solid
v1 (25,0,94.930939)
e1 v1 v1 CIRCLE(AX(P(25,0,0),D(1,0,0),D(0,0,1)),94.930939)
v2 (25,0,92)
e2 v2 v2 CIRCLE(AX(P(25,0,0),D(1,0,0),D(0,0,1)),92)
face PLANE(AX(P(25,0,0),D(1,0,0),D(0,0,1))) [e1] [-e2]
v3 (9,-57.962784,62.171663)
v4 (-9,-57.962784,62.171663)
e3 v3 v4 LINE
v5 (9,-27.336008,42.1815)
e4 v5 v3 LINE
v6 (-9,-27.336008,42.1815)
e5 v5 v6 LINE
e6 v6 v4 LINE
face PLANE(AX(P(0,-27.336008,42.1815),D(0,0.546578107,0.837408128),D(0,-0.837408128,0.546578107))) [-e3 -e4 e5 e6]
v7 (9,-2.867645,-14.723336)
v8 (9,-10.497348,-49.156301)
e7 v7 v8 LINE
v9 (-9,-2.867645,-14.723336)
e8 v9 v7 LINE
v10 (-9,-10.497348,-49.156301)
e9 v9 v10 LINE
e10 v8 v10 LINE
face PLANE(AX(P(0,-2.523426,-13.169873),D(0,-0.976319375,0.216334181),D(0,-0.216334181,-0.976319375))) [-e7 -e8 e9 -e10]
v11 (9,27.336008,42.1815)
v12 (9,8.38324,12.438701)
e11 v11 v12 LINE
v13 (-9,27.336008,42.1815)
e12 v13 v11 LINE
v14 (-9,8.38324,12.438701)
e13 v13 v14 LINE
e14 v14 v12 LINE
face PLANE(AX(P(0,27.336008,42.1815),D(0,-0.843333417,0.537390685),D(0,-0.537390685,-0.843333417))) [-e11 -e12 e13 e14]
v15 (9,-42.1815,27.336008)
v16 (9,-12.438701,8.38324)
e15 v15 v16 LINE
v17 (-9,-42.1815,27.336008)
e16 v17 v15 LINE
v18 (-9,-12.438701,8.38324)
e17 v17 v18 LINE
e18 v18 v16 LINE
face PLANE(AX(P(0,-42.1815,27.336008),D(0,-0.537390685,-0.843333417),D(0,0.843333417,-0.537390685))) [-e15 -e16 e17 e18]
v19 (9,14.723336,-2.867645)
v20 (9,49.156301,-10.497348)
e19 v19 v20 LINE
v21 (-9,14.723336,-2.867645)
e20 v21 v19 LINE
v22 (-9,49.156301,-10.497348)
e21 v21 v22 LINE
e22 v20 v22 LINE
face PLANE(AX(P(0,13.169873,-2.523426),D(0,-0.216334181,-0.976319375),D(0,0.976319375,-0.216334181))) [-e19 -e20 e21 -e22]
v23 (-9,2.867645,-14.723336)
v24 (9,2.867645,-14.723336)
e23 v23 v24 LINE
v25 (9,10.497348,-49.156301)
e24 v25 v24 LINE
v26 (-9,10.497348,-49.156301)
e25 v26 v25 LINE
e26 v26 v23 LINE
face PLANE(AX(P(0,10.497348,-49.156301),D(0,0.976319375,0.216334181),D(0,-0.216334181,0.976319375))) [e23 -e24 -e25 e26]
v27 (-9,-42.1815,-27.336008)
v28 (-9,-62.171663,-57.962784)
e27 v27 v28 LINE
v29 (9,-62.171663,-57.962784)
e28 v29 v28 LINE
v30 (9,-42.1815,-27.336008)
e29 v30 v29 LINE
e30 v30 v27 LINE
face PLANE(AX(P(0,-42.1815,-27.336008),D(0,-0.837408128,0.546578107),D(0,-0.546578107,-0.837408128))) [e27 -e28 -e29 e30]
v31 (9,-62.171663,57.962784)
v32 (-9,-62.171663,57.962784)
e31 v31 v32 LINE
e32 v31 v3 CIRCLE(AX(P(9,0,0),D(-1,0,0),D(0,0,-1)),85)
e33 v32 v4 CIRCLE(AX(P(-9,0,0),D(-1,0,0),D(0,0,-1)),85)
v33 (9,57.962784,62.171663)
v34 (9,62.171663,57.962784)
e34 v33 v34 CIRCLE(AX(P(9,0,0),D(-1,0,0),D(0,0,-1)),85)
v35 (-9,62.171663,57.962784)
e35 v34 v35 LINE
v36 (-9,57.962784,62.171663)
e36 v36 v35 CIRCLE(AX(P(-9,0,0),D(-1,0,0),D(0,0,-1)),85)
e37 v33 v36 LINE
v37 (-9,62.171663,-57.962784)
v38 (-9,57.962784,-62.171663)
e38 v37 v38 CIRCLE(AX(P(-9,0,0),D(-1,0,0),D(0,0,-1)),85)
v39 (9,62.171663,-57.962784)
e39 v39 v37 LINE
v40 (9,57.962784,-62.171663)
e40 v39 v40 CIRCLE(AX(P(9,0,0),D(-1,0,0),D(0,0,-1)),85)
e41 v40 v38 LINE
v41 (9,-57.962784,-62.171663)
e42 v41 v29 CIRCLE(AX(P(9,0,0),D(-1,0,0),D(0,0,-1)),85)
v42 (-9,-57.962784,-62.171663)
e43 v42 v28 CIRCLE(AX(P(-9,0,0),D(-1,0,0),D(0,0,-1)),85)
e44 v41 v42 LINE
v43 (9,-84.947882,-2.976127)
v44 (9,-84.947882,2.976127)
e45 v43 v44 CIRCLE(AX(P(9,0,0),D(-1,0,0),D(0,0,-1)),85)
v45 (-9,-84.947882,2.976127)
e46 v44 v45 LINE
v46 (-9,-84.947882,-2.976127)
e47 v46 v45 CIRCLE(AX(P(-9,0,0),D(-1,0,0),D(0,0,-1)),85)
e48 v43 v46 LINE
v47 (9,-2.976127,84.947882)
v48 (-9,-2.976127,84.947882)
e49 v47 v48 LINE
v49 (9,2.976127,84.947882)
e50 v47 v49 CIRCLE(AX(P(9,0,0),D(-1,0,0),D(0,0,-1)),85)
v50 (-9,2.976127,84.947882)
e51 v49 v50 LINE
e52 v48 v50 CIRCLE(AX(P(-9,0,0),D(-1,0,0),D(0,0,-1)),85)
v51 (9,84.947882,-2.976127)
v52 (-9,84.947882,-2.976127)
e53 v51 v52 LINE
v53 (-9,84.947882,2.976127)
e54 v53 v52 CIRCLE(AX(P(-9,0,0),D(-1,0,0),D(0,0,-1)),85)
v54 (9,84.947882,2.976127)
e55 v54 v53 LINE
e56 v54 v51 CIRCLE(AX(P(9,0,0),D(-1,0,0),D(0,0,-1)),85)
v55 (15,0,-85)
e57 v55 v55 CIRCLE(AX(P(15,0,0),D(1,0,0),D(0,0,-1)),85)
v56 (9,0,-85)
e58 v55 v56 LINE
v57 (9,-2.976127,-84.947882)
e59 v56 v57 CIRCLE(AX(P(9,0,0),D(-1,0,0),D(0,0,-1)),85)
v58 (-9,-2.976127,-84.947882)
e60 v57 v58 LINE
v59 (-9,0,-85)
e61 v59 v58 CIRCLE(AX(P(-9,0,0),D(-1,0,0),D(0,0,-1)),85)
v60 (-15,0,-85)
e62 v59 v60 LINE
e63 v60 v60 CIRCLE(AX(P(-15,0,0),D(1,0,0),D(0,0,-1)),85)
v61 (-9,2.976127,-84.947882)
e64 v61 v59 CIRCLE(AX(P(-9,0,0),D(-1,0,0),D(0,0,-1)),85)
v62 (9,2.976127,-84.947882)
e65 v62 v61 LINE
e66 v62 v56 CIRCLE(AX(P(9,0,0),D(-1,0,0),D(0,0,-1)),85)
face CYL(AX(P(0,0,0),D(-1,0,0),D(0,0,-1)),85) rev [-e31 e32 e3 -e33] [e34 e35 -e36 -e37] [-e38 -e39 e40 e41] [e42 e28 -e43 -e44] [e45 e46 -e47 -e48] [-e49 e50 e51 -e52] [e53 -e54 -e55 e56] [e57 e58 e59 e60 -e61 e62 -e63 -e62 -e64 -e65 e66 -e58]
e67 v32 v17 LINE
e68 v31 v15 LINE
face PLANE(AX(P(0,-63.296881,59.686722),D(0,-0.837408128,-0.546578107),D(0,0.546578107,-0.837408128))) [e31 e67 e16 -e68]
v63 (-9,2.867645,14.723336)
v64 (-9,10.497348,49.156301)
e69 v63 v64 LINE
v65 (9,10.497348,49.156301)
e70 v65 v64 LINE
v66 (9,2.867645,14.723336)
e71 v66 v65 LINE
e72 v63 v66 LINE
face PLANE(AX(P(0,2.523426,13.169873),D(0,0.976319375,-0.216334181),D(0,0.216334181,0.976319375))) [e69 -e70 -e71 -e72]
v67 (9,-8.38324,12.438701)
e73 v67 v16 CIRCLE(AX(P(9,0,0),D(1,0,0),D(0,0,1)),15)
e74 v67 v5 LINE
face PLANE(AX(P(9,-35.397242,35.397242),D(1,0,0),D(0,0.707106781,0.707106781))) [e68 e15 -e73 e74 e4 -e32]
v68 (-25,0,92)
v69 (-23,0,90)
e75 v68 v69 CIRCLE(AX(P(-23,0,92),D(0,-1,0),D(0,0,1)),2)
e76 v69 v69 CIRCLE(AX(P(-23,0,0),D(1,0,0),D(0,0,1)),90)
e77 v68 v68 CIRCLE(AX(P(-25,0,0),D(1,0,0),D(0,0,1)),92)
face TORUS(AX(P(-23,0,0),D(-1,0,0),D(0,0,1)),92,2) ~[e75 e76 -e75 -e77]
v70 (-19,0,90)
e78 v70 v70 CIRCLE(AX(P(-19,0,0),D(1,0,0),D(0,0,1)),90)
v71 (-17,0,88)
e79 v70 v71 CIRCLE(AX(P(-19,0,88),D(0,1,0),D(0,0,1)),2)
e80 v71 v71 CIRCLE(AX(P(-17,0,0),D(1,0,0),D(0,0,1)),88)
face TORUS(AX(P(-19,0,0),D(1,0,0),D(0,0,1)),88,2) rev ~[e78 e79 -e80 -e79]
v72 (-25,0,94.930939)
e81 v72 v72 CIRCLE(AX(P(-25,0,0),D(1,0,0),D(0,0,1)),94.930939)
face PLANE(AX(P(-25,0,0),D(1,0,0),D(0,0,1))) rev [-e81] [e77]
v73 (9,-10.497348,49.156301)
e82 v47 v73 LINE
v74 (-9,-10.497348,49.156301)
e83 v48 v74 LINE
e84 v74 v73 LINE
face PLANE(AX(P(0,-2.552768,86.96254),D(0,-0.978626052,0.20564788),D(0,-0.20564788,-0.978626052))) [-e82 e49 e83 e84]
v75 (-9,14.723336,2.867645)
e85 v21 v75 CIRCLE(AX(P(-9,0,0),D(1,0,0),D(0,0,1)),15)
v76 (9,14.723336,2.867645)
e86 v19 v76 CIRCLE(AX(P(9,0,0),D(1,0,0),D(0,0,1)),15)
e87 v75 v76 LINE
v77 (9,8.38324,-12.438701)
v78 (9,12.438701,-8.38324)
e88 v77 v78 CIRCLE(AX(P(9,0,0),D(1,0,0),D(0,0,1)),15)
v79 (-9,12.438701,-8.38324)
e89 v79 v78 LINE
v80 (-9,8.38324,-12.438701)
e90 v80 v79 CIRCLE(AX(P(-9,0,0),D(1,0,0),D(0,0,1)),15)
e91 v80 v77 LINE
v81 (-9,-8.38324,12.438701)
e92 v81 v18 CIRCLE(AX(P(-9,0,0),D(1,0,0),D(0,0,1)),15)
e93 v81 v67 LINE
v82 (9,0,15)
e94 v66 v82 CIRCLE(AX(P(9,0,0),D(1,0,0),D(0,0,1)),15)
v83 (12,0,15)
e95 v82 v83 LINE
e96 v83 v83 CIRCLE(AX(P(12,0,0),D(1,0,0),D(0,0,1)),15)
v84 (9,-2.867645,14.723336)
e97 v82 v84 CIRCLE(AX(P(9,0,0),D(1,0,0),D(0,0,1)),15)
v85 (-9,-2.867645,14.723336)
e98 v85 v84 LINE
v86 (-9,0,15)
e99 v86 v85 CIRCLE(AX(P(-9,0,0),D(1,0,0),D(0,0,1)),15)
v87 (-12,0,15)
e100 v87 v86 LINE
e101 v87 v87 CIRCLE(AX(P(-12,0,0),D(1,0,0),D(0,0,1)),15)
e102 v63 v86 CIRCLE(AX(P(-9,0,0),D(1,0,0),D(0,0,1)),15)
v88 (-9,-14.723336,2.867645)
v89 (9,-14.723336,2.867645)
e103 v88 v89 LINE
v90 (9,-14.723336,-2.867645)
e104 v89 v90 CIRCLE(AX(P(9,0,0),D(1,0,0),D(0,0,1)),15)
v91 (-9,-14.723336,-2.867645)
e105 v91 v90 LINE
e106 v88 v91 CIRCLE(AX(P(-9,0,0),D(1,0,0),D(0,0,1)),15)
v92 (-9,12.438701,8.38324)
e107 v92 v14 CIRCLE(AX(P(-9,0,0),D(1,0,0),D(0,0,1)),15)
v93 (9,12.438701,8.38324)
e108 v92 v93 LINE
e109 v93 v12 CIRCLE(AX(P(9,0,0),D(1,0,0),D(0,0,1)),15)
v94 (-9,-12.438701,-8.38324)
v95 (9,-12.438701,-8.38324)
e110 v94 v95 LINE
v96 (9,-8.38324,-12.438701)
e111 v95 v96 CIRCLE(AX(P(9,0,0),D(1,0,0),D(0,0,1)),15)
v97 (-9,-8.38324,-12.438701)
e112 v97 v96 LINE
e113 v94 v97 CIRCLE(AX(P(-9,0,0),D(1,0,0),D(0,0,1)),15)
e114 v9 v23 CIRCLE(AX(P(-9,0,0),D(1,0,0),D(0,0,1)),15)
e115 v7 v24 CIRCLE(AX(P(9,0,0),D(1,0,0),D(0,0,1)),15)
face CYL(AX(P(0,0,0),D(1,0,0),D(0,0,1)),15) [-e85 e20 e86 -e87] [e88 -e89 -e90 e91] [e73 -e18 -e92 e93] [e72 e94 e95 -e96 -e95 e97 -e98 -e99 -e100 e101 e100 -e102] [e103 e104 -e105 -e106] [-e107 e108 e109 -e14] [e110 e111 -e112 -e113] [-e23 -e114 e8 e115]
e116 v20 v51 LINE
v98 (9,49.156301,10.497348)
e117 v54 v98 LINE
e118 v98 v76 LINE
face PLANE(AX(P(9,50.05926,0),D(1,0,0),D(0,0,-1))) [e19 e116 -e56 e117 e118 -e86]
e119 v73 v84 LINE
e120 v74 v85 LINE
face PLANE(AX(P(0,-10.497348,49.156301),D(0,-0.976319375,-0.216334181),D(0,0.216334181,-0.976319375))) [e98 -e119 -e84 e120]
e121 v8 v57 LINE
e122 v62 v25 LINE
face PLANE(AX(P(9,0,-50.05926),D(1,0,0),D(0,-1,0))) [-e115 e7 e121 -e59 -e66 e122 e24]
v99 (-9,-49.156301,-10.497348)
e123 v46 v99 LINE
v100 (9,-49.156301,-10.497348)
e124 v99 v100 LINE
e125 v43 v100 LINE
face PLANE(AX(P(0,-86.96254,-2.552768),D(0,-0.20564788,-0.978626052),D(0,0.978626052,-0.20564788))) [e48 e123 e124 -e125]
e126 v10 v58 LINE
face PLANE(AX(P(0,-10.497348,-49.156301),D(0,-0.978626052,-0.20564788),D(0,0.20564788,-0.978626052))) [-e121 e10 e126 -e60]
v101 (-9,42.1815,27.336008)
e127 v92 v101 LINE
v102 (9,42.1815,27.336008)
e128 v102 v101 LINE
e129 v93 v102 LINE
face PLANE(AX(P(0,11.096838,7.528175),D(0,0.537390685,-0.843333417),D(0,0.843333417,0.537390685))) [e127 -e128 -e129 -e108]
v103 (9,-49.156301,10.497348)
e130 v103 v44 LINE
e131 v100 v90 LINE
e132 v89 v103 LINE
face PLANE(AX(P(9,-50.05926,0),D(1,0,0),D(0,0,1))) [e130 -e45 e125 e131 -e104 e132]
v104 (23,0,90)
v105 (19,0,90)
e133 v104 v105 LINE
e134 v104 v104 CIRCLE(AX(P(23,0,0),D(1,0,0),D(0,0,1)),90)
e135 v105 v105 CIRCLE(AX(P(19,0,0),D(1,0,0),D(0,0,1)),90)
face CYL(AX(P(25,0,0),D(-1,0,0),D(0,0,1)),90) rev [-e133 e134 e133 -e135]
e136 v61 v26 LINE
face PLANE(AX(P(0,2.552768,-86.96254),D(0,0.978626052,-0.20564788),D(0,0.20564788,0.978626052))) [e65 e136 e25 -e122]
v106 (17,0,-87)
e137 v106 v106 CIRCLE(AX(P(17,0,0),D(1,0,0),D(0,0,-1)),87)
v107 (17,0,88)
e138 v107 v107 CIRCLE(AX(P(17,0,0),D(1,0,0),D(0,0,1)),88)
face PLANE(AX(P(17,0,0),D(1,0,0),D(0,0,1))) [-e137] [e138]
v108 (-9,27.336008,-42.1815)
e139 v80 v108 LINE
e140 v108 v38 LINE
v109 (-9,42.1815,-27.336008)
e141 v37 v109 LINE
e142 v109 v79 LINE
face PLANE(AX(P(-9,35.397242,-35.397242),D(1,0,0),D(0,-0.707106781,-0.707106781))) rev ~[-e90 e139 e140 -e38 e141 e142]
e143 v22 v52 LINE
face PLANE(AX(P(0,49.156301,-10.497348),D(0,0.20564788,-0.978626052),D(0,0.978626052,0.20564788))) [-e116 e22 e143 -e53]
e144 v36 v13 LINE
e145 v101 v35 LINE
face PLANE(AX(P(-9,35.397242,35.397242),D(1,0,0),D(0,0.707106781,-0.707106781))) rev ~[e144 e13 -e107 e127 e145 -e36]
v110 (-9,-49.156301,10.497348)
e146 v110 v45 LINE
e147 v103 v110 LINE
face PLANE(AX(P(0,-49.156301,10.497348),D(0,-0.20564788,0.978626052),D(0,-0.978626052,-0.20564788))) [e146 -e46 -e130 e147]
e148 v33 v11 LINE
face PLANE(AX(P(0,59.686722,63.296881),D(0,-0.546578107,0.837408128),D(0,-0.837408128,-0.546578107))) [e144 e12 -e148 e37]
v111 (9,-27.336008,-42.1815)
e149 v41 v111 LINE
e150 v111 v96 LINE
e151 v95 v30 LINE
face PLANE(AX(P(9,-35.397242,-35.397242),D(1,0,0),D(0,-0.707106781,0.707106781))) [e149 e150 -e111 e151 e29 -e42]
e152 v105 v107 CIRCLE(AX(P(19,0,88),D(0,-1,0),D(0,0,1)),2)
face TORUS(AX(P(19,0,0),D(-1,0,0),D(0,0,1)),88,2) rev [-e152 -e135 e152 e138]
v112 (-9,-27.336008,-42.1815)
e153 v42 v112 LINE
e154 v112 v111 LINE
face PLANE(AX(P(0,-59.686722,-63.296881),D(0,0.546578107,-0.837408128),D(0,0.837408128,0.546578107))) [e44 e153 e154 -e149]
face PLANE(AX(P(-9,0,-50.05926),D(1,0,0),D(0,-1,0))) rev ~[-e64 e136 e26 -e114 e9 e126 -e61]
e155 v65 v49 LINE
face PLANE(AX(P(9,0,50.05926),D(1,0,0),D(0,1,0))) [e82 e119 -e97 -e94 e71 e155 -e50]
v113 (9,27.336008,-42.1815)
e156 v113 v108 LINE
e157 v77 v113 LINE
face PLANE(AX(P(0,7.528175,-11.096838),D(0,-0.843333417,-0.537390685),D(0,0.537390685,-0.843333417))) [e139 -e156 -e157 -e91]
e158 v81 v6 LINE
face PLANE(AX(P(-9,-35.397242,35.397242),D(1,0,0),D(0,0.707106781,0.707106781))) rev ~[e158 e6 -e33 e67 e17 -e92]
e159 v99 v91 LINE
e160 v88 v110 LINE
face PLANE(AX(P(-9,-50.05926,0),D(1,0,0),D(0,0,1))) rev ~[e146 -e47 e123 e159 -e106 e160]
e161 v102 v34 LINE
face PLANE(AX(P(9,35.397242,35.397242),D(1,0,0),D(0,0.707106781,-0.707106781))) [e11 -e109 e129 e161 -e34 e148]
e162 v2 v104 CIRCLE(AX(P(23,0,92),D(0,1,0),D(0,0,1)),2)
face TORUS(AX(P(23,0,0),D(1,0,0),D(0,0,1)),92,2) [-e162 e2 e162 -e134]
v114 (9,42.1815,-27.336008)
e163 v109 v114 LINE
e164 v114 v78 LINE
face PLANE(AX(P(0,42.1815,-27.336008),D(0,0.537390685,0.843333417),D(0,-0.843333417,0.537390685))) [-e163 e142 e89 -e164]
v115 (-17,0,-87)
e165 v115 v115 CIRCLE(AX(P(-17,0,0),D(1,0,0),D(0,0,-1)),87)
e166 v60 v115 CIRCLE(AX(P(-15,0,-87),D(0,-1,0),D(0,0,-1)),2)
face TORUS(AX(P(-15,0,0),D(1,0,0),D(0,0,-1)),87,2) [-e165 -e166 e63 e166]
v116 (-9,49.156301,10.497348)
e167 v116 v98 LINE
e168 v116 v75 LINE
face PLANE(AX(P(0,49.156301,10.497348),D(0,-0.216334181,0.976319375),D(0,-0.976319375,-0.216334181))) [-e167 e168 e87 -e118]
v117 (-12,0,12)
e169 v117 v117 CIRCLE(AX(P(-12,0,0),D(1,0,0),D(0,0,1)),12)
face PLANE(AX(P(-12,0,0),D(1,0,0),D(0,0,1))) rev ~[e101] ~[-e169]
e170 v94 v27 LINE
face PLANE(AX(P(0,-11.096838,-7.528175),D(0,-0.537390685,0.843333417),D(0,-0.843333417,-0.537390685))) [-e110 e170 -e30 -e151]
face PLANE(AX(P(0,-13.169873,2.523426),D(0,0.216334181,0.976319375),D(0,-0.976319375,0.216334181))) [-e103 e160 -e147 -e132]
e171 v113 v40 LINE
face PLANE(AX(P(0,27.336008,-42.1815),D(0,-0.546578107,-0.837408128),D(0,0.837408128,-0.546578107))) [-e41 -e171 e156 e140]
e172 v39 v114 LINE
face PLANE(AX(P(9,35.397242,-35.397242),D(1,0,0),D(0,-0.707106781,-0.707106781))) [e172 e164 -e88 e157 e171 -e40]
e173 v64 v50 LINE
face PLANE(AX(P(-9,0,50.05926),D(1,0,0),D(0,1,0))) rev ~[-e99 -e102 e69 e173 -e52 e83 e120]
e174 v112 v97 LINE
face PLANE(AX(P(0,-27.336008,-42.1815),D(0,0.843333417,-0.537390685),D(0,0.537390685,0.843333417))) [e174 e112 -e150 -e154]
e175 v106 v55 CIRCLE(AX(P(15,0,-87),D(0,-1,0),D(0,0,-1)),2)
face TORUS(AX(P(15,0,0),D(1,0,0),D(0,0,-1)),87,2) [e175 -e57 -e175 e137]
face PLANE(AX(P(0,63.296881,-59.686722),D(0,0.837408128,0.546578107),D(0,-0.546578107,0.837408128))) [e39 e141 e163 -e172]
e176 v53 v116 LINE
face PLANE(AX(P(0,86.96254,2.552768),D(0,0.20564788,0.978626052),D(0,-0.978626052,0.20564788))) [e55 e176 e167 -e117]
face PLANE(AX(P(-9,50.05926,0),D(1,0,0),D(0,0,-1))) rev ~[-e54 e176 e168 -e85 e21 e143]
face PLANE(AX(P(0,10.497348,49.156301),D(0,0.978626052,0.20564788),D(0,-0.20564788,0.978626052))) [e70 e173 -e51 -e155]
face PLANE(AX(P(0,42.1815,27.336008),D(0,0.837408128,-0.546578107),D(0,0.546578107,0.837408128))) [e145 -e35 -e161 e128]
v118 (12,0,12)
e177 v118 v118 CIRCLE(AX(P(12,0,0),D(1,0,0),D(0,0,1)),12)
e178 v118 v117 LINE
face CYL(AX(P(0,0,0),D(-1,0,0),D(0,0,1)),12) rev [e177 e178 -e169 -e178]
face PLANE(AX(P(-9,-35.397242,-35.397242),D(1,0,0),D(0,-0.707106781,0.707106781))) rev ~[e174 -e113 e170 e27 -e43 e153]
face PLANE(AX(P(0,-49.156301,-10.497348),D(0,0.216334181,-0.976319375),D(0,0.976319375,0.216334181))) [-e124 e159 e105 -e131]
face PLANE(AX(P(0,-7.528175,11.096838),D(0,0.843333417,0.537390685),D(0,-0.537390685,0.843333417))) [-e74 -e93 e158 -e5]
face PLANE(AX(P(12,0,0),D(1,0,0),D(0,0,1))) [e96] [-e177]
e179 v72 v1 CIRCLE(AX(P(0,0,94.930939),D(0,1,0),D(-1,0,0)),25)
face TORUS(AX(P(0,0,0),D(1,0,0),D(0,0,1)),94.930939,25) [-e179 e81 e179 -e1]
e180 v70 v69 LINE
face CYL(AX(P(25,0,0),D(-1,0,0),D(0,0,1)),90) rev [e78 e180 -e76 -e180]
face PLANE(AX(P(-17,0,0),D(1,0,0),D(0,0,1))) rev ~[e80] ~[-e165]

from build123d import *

# Parameters (mm, degrees)
SKETCH2_R           = 90
SKETCH2_R_2         = 85
BOSS_EXTRUDE1_DEPTH = 17
SKETCH3_R           = 15
SKETCH3_R_2         = 12
BOSS_EXTRUDE2_DEPTH = 12
FILLET1_R           = 2
BOSS_EXTRUDE3_DEPTH = 9
CIRPATTERN1_COUNT   = 8


with BuildPart() as part:
    # Sketch1 → Revolve1 (revolve)
    with BuildSketch(Plane.XY, mode=Mode.PRIVATE) as revolve1_sk:
        with BuildLine():
            Line((25, 94.930938799), (25, 90))
            Line((25, 90), (-25, 90))
            Line((-25, 90), (-25, 94.930938799))
            ThreePointArc((-25, 94.930938799), (0, 119.930938799), (25, 94.930938799))
        make_face()
    revolve(revolve1_sk.sketch.rotate(Axis((0, 0, 0), (1, 0, 0)), 90), axis=Axis((0, 0, 0), (1, 0, 0)))

    # Sketch2 → Boss-Extrude1 (add, symmetric)
    with BuildSketch(Plane(origin=(0, 0, 0), x_dir=(0, 0, -1), z_dir=(1, 0, 0))):
        with Locations(Location((0, 0, 0), (0, 0, 180))):
            Circle(SKETCH2_R)
        Circle(SKETCH2_R_2, mode=Mode.SUBTRACT)
    extrude(amount=BOSS_EXTRUDE1_DEPTH, both=True)

    # Fillet1
    fillet1_edges = [part.edges().sort_by_distance(p)[0] for p in [
        (-17, 0, -90),
        (17, 0, -90),
        (-17, 0, 85),
        (17, 0, 85),
        (-25, 0, -90),
        (25, 0, -90),
    ]]
    fillet(fillet1_edges, radius=FILLET1_R)



with BuildPart() as body_2:
    # Sketch3 → Boss-Extrude2 (new, symmetric)
    with BuildSketch(Plane(origin=(0, 0, 0), x_dir=(0, 0, -1), z_dir=(1, 0, 0))):
        with Locations(Location((0, 0, 0), (0, 0, 180))):
            Circle(SKETCH3_R)
        with Locations(Location((0, 0, 0), (0, 0, 180))):
            Circle(SKETCH3_R_2, mode=Mode.SUBTRACT)
    extrude(amount=BOSS_EXTRUDE2_DEPTH, both=True)


with BuildPart() as part_1:
    add(part.part)

    add(body_2.part)  # Boss-Extrude3 merges body 2
    # Sketch4 → Boss-Extrude3 (add, symmetric)
    with BuildSketch(Plane(origin=(0, 0, 0), x_dir=(0, 0, -1), z_dir=(1, 0, 0))):
        Polygon((-2.552768196, 86.962540065), (-10.497348074, 49.156301409), (-2.523426033, 13.169872653), (2.523426033, 13.169872653), (10.497348074, 49.156301409), (2.552768196, 86.962540065), align=None)
    boss_extrude3 = extrude(amount=BOSS_EXTRUDE3_DEPTH, both=True)

    # CirPattern1: Boss-Extrude3 ×8 about axis
    cirpattern1_axis = Axis((0, 0, 0), (1, 0, 0))
    for i in range(1, CIRPATTERN1_COUNT):
        add(boss_extrude3.rotate(cirpattern1_axis, i * 360 / CIRPATTERN1_COUNT))


solid = part_1.part
